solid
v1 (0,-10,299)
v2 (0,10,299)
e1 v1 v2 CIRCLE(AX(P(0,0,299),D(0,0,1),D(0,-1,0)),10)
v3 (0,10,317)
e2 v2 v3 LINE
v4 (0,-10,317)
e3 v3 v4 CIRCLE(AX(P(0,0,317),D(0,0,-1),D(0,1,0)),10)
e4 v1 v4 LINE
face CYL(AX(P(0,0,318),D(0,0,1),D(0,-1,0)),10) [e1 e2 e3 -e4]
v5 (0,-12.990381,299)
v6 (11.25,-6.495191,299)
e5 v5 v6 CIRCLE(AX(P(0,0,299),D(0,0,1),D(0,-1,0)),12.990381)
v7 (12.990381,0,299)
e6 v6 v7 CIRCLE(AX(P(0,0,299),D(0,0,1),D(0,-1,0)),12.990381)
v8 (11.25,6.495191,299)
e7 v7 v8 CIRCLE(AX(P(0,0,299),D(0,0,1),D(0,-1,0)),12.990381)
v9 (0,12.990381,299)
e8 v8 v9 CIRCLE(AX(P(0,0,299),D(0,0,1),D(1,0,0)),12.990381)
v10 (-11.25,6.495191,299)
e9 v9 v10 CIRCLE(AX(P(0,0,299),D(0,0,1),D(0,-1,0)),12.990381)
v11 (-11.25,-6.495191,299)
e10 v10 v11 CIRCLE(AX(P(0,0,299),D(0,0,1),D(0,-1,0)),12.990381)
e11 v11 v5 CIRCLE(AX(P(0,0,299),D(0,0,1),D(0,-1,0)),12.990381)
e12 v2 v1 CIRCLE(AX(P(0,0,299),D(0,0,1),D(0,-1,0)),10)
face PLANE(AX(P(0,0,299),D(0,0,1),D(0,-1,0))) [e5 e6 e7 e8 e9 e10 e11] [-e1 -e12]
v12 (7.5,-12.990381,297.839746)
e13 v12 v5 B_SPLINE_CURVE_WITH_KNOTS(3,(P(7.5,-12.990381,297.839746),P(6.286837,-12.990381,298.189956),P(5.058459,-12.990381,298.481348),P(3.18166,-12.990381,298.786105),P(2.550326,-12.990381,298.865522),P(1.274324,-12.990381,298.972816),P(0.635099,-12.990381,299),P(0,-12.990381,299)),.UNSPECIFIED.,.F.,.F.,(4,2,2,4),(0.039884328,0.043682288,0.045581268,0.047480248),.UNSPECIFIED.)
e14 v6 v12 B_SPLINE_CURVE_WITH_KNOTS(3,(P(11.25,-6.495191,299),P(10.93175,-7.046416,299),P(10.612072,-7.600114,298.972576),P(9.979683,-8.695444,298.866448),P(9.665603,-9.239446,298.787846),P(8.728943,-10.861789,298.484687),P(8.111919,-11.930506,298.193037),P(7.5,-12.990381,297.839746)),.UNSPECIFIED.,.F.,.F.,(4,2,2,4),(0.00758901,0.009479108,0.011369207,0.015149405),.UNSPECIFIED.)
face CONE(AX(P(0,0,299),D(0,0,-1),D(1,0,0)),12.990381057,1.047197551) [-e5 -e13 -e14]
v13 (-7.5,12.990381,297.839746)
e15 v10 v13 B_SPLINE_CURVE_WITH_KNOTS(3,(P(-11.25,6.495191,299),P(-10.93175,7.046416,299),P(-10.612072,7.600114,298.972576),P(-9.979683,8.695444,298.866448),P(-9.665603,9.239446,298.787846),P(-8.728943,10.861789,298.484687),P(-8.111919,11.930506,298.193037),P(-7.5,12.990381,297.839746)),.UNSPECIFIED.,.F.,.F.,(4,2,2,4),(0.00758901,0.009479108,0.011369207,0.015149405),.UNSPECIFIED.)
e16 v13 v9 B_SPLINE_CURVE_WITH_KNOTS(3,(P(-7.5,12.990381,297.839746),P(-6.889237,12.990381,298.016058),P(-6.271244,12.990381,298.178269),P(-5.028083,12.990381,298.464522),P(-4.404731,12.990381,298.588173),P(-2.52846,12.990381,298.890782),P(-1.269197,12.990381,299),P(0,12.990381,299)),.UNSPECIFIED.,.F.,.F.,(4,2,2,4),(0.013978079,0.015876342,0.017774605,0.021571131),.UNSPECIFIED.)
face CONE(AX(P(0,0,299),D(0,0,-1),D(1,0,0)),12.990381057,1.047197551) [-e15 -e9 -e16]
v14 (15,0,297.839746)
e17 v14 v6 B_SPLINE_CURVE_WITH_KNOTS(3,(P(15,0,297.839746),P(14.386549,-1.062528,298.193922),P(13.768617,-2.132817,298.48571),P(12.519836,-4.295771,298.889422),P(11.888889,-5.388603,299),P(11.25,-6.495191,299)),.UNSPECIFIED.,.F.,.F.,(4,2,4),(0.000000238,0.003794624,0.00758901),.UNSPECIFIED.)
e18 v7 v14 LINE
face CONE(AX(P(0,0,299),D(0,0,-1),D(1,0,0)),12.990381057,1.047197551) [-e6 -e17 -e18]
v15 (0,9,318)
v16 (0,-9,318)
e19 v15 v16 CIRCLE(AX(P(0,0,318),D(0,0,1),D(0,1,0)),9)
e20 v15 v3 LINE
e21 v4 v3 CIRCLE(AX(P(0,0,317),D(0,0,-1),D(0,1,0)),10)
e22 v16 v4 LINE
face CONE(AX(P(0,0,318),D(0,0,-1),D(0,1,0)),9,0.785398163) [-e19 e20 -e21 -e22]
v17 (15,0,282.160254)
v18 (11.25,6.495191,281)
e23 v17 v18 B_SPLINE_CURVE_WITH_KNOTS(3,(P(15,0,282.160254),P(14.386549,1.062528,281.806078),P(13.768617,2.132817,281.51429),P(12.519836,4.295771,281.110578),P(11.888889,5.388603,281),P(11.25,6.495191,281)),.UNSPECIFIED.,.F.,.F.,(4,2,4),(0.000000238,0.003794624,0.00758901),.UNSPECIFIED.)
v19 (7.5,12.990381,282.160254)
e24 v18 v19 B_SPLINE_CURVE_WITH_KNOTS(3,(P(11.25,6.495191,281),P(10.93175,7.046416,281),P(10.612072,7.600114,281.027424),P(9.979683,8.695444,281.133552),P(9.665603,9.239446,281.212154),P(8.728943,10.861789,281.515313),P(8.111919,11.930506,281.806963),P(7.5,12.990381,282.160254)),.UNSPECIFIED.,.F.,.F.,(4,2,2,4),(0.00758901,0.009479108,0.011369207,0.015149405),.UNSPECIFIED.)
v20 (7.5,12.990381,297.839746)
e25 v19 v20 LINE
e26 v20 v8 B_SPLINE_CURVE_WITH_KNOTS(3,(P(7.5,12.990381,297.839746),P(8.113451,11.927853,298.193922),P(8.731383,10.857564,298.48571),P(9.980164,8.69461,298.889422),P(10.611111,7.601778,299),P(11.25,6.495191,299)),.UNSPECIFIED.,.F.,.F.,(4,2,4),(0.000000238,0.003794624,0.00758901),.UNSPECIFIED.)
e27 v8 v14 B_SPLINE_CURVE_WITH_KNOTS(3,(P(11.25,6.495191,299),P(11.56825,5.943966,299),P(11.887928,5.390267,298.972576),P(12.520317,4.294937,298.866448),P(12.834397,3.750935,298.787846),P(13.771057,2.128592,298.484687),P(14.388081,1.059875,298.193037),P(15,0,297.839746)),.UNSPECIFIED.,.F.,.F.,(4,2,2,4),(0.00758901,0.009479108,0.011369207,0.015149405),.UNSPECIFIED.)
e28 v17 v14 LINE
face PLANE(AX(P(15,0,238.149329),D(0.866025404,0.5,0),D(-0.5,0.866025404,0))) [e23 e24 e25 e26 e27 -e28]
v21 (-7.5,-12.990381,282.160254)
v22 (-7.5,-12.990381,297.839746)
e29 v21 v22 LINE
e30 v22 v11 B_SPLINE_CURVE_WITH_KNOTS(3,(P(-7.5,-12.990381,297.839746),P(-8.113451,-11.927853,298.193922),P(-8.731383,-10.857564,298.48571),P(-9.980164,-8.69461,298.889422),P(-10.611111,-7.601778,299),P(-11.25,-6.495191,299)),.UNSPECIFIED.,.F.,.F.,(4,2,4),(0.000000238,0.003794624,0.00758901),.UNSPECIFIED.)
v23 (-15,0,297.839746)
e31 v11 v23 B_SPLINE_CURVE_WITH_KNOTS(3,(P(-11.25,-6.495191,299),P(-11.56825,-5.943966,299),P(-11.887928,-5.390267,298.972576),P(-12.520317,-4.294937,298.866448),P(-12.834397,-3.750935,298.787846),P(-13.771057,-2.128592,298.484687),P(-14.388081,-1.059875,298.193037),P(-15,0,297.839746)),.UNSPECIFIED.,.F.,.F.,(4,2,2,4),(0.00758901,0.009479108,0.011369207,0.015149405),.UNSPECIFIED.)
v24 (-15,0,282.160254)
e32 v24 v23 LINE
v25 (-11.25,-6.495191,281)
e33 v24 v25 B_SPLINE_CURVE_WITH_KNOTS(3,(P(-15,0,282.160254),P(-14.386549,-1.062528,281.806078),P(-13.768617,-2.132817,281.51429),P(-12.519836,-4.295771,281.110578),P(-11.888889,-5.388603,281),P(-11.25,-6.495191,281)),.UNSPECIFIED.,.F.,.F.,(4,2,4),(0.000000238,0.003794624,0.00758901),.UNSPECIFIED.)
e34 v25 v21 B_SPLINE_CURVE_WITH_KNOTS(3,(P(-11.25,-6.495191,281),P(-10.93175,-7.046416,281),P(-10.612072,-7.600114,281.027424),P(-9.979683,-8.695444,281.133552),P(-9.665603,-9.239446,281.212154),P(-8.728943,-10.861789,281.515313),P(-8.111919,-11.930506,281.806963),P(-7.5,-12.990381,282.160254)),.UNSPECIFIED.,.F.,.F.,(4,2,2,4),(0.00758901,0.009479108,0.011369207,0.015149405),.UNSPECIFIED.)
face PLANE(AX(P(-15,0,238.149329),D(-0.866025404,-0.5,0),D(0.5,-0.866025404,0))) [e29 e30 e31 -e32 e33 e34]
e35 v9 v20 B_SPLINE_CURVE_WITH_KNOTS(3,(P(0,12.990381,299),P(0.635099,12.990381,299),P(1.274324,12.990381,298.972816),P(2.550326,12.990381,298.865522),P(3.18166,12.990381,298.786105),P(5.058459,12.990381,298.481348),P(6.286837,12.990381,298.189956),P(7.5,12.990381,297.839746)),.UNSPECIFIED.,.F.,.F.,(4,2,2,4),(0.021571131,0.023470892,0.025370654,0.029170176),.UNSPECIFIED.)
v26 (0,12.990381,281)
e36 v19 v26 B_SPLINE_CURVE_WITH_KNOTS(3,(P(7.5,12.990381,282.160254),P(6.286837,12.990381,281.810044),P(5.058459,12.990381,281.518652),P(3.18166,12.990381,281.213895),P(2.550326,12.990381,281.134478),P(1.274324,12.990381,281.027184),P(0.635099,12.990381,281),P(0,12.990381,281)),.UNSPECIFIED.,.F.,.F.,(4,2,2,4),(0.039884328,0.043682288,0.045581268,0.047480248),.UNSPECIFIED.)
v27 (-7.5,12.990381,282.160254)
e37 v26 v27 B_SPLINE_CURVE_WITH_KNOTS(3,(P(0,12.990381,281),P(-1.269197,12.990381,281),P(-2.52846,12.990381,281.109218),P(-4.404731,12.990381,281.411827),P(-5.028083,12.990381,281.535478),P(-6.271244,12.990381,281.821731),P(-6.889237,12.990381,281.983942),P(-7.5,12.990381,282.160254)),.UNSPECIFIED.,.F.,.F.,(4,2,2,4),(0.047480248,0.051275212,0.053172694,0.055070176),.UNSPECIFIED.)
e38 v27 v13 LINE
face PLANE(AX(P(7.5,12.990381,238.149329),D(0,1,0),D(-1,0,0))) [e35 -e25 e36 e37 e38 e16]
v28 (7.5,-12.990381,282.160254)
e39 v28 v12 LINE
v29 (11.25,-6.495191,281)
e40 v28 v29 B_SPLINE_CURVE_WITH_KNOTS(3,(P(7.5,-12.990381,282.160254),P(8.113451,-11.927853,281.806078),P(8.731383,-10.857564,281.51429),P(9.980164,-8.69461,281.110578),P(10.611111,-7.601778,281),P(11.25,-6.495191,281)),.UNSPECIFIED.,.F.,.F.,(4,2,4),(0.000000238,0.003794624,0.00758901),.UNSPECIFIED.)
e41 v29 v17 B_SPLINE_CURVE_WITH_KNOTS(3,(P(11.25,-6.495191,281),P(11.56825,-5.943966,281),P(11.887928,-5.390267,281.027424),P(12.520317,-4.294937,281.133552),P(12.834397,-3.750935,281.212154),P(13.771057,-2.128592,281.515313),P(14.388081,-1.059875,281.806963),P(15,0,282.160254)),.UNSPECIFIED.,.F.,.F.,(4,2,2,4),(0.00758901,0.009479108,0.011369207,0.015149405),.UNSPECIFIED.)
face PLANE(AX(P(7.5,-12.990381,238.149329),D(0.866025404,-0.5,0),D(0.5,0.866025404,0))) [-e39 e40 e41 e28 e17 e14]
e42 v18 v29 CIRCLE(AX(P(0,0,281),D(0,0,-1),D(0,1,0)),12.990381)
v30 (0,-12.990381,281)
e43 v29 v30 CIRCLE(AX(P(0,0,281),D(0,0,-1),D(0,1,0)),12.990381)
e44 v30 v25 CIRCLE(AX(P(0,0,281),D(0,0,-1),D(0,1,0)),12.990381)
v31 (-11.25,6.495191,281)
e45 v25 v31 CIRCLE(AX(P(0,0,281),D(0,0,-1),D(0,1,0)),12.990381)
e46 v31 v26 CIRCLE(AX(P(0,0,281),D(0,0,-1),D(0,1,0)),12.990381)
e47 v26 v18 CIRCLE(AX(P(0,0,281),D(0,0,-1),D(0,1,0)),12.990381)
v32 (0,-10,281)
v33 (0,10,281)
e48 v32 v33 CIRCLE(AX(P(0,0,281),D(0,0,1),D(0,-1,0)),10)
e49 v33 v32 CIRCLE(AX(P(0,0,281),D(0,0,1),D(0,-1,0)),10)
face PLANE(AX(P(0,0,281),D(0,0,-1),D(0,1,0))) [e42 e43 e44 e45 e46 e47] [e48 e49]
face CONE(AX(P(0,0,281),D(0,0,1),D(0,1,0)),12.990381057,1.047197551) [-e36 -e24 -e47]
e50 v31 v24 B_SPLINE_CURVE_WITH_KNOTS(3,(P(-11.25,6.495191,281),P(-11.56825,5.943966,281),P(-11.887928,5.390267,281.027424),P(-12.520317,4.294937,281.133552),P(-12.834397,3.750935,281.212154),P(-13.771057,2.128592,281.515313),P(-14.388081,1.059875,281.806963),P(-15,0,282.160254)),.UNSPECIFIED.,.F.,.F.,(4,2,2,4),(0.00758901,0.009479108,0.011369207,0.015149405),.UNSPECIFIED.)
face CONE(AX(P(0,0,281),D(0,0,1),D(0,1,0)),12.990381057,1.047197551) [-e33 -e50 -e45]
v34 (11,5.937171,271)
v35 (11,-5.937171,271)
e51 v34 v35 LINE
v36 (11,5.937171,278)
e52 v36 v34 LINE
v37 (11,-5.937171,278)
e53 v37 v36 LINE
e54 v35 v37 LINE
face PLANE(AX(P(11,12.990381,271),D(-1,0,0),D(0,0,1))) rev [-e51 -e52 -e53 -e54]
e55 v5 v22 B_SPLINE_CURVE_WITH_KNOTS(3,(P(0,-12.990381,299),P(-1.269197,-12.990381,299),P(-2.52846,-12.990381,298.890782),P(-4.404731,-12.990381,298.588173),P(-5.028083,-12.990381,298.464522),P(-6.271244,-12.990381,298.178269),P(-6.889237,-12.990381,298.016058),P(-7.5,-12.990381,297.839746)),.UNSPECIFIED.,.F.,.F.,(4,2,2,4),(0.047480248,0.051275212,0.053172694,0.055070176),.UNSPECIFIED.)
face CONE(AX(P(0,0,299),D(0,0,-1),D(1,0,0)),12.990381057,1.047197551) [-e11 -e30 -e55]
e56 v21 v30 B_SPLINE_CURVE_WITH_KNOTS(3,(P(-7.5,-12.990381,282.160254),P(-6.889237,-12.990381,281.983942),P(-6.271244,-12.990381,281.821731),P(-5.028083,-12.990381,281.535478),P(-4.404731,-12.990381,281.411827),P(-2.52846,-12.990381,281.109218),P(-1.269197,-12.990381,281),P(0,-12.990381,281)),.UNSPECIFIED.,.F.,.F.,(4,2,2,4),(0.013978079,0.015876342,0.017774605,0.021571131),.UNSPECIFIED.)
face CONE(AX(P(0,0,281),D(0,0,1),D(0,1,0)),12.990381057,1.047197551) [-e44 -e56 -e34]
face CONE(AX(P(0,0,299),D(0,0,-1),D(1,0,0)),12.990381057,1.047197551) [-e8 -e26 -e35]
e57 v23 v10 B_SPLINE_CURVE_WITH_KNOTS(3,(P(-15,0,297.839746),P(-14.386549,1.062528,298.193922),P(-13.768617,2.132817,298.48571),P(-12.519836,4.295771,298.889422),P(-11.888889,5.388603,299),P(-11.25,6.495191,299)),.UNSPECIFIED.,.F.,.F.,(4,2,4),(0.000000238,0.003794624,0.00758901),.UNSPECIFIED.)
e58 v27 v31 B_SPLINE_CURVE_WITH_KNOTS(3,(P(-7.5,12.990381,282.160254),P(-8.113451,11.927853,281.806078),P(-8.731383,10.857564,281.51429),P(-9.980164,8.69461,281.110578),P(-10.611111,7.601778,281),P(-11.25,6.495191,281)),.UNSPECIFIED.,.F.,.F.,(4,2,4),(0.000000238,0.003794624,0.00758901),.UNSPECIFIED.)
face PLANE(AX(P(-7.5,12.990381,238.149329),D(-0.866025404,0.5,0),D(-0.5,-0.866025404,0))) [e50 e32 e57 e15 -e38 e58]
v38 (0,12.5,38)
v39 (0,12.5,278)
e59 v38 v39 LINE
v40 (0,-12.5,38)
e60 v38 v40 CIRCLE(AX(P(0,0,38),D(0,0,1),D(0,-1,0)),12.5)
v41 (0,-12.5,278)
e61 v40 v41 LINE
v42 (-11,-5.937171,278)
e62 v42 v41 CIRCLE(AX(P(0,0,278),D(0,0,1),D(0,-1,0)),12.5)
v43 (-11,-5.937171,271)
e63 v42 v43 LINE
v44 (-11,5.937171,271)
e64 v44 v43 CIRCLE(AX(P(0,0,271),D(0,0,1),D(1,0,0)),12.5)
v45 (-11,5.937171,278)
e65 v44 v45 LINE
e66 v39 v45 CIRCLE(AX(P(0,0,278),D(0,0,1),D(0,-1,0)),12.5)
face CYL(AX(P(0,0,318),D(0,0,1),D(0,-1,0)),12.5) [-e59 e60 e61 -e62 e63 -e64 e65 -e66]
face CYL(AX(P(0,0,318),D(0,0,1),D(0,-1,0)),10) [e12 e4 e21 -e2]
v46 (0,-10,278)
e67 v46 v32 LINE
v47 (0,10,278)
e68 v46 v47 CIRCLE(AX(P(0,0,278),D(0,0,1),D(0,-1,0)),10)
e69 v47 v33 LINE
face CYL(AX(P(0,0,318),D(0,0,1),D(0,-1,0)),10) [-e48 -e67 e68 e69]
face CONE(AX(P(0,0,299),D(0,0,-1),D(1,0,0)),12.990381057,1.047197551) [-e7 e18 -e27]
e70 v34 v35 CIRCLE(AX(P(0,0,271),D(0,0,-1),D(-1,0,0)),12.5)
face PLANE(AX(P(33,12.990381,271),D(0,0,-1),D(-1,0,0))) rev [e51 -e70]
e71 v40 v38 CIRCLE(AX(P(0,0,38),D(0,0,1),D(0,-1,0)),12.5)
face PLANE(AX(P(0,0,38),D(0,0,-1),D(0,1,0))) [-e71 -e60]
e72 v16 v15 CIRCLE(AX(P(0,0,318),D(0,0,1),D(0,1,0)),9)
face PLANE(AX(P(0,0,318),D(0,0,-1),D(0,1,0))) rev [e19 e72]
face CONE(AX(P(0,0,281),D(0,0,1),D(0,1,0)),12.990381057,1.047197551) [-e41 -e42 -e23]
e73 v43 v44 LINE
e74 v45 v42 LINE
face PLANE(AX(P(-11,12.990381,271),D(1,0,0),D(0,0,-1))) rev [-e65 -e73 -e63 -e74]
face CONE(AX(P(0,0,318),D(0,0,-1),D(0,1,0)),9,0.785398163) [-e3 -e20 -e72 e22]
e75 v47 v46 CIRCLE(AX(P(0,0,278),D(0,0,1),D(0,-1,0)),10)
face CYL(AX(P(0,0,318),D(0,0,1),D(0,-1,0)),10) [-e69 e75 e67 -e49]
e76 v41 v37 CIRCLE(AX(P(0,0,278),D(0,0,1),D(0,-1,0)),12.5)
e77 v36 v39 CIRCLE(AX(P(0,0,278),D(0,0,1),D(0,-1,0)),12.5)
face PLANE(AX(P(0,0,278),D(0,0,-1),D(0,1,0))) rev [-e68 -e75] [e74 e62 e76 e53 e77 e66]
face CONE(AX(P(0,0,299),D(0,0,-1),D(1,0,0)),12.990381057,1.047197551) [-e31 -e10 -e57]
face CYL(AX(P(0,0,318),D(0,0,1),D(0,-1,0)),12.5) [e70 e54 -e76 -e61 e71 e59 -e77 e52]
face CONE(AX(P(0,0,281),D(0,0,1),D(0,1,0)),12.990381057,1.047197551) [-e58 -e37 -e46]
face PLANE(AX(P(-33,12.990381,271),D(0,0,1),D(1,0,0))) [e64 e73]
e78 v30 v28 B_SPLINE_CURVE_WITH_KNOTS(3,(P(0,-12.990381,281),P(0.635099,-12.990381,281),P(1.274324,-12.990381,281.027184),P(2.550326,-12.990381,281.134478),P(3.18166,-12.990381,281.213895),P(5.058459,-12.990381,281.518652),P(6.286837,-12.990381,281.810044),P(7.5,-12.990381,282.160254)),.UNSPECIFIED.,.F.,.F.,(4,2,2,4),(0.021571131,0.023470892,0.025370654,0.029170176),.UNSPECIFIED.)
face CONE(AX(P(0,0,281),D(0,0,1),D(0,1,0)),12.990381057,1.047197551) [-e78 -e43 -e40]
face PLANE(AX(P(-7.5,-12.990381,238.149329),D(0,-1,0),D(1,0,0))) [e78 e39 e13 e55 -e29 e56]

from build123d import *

# Parameters (mm, degrees)
SKETCH5_OUTSIDE_W  = 88.64
SKETCH5_OUTSIDE_H  = 88.64
CUT_EXTRUDE1_DEPTH = 18
SKETCH6_OUTSIDE_W  = 123.2
SKETCH6_OUTSIDE_H  = 119.18
SKETCH6_OUTSIDE_R  = 12.990381057
CUT_EXTRUDE2_DEPTH = 10
CUT_EXTRUDE2_DRAFT = -60
SKETCH7_OUTSIDE_W  = 123.2
SKETCH7_OUTSIDE_H  = 119.18
SKETCH7_OUTSIDE_R  = 12.990381057
CUT_EXTRUDE3_DEPTH = 10
CUT_EXTRUDE3_DRAFT = -60
SKETCH9_W          = 22
SKETCH9_H          = 25.980762114
CUT_EXTRUDE4_DEPTH = 7
CHAMFER1_SIZE      = 1


with BuildPart() as part:
    # Sketch3 → Revolve1 (revolve)
    with BuildSketch(Plane(origin=(0, 0, 0), x_dir=(0, 0, -1), z_dir=(1, 0, 0)), mode=Mode.PRIVATE) as revolve1_sk:
        Polygon((-38, 12.5), (-38, 0), (-318, 0), (-318, 10), (-299, 10), (-299, 15), (-281, 15), (-281, 10), (-278, 10), (-278, 12.5), align=None)
    revolve(revolve1_sk.sketch.rotate(Axis((0, 0, 318), (0, 0, -1)), 180), axis=Axis((0, 0, 318), (0, 0, -1)))

    # Sketch5 outside → Cut-Extrude1 (cut)
    with BuildSketch(Plane.XY.offset(299)):
        Rectangle(SKETCH5_OUTSIDE_W, SKETCH5_OUTSIDE_H)
        Polygon((7.5, 12.990381057), (-7.5, 12.990381057), (-15, 0), (-7.5, -12.990381057), (7.5, -12.990381057), (15, 0), align=None, mode=Mode.SUBTRACT)
    extrude(amount=-CUT_EXTRUDE1_DEPTH, mode=Mode.SUBTRACT)


with BuildPart() as cut_extrude2_tool:
    # Sketch6 outside → Cut-Extrude2 (with draft: the straight prism first)
    with BuildSketch(Plane.XY.offset(299)):
        Rectangle(SKETCH6_OUTSIDE_W, SKETCH6_OUTSIDE_H)
        Circle(SKETCH6_OUTSIDE_R, mode=Mode.SUBTRACT)
    extrude(amount=-CUT_EXTRUDE2_DEPTH)
    # Cut-Extrude2: the draft: its side faces are tilted about the plane it starts from
    cut_extrude2_sides = [cut_extrude2_tool.faces().sort_by_distance(p)[0] for p in [
        (0, -59.59, 294),
        (61.6, 0, 294),
        (0, 59.59, 294),
        (-61.6, 0, 294),
        (-12.990381057, 0, 294),
    ]]
    draft(cut_extrude2_sides, Plane.XY.offset(299), CUT_EXTRUDE2_DRAFT)


with BuildPart() as part_1:
    add(part.part)

    # Cut-Extrude2: cut by cut_extrude2_tool
    add(cut_extrude2_tool.part, mode=Mode.SUBTRACT)


with BuildPart() as cut_extrude3_tool:
    # Sketch7 outside → Cut-Extrude3 (with draft: the straight prism first)
    with BuildSketch(Plane(origin=(0, 0, 281), x_dir=(-1, 0, 0), z_dir=(0, 0, -1))):
        Rectangle(SKETCH7_OUTSIDE_W, SKETCH7_OUTSIDE_H)
        Circle(SKETCH7_OUTSIDE_R, mode=Mode.SUBTRACT)
    extrude(amount=-CUT_EXTRUDE3_DEPTH)
    # Cut-Extrude3: the draft: its side faces are tilted about the plane it starts from
    cut_extrude3_sides = [cut_extrude3_tool.faces().sort_by_distance(p)[0] for p in [
        (0, -59.59, 286),
        (-61.6, 0, 286),
        (0, 59.59, 286),
        (61.6, 0, 286),
        (12.990381057, 0, 286),
    ]]
    draft(cut_extrude3_sides, Plane(origin=(0, 0, 281), x_dir=(-1, 0, 0), z_dir=(0, 0, -1)), CUT_EXTRUDE3_DRAFT)


with BuildPart() as part_2:
    add(part_1.part)

    # Cut-Extrude3: cut by cut_extrude3_tool
    add(cut_extrude3_tool.part, mode=Mode.SUBTRACT)

    # Sketch9 → Cut-Extrude4 (cut)
    with BuildSketch(Plane.XY.offset(278)):
        with Locations((-22, 0)):
            Rectangle(SKETCH9_W, SKETCH9_H)
        with Locations((22, 0)):
            Rectangle(SKETCH9_W, SKETCH9_H)
    extrude(amount=-CUT_EXTRUDE4_DEPTH, mode=Mode.SUBTRACT)

    # Chamfer1
    chamfer1_edges = [part_2.edges().sort_by_distance(p)[0] for p in [
        (0, 10, 318),
    ]]
    chamfer(chamfer1_edges, length=CHAMFER1_SIZE)


solid = part_2.part
